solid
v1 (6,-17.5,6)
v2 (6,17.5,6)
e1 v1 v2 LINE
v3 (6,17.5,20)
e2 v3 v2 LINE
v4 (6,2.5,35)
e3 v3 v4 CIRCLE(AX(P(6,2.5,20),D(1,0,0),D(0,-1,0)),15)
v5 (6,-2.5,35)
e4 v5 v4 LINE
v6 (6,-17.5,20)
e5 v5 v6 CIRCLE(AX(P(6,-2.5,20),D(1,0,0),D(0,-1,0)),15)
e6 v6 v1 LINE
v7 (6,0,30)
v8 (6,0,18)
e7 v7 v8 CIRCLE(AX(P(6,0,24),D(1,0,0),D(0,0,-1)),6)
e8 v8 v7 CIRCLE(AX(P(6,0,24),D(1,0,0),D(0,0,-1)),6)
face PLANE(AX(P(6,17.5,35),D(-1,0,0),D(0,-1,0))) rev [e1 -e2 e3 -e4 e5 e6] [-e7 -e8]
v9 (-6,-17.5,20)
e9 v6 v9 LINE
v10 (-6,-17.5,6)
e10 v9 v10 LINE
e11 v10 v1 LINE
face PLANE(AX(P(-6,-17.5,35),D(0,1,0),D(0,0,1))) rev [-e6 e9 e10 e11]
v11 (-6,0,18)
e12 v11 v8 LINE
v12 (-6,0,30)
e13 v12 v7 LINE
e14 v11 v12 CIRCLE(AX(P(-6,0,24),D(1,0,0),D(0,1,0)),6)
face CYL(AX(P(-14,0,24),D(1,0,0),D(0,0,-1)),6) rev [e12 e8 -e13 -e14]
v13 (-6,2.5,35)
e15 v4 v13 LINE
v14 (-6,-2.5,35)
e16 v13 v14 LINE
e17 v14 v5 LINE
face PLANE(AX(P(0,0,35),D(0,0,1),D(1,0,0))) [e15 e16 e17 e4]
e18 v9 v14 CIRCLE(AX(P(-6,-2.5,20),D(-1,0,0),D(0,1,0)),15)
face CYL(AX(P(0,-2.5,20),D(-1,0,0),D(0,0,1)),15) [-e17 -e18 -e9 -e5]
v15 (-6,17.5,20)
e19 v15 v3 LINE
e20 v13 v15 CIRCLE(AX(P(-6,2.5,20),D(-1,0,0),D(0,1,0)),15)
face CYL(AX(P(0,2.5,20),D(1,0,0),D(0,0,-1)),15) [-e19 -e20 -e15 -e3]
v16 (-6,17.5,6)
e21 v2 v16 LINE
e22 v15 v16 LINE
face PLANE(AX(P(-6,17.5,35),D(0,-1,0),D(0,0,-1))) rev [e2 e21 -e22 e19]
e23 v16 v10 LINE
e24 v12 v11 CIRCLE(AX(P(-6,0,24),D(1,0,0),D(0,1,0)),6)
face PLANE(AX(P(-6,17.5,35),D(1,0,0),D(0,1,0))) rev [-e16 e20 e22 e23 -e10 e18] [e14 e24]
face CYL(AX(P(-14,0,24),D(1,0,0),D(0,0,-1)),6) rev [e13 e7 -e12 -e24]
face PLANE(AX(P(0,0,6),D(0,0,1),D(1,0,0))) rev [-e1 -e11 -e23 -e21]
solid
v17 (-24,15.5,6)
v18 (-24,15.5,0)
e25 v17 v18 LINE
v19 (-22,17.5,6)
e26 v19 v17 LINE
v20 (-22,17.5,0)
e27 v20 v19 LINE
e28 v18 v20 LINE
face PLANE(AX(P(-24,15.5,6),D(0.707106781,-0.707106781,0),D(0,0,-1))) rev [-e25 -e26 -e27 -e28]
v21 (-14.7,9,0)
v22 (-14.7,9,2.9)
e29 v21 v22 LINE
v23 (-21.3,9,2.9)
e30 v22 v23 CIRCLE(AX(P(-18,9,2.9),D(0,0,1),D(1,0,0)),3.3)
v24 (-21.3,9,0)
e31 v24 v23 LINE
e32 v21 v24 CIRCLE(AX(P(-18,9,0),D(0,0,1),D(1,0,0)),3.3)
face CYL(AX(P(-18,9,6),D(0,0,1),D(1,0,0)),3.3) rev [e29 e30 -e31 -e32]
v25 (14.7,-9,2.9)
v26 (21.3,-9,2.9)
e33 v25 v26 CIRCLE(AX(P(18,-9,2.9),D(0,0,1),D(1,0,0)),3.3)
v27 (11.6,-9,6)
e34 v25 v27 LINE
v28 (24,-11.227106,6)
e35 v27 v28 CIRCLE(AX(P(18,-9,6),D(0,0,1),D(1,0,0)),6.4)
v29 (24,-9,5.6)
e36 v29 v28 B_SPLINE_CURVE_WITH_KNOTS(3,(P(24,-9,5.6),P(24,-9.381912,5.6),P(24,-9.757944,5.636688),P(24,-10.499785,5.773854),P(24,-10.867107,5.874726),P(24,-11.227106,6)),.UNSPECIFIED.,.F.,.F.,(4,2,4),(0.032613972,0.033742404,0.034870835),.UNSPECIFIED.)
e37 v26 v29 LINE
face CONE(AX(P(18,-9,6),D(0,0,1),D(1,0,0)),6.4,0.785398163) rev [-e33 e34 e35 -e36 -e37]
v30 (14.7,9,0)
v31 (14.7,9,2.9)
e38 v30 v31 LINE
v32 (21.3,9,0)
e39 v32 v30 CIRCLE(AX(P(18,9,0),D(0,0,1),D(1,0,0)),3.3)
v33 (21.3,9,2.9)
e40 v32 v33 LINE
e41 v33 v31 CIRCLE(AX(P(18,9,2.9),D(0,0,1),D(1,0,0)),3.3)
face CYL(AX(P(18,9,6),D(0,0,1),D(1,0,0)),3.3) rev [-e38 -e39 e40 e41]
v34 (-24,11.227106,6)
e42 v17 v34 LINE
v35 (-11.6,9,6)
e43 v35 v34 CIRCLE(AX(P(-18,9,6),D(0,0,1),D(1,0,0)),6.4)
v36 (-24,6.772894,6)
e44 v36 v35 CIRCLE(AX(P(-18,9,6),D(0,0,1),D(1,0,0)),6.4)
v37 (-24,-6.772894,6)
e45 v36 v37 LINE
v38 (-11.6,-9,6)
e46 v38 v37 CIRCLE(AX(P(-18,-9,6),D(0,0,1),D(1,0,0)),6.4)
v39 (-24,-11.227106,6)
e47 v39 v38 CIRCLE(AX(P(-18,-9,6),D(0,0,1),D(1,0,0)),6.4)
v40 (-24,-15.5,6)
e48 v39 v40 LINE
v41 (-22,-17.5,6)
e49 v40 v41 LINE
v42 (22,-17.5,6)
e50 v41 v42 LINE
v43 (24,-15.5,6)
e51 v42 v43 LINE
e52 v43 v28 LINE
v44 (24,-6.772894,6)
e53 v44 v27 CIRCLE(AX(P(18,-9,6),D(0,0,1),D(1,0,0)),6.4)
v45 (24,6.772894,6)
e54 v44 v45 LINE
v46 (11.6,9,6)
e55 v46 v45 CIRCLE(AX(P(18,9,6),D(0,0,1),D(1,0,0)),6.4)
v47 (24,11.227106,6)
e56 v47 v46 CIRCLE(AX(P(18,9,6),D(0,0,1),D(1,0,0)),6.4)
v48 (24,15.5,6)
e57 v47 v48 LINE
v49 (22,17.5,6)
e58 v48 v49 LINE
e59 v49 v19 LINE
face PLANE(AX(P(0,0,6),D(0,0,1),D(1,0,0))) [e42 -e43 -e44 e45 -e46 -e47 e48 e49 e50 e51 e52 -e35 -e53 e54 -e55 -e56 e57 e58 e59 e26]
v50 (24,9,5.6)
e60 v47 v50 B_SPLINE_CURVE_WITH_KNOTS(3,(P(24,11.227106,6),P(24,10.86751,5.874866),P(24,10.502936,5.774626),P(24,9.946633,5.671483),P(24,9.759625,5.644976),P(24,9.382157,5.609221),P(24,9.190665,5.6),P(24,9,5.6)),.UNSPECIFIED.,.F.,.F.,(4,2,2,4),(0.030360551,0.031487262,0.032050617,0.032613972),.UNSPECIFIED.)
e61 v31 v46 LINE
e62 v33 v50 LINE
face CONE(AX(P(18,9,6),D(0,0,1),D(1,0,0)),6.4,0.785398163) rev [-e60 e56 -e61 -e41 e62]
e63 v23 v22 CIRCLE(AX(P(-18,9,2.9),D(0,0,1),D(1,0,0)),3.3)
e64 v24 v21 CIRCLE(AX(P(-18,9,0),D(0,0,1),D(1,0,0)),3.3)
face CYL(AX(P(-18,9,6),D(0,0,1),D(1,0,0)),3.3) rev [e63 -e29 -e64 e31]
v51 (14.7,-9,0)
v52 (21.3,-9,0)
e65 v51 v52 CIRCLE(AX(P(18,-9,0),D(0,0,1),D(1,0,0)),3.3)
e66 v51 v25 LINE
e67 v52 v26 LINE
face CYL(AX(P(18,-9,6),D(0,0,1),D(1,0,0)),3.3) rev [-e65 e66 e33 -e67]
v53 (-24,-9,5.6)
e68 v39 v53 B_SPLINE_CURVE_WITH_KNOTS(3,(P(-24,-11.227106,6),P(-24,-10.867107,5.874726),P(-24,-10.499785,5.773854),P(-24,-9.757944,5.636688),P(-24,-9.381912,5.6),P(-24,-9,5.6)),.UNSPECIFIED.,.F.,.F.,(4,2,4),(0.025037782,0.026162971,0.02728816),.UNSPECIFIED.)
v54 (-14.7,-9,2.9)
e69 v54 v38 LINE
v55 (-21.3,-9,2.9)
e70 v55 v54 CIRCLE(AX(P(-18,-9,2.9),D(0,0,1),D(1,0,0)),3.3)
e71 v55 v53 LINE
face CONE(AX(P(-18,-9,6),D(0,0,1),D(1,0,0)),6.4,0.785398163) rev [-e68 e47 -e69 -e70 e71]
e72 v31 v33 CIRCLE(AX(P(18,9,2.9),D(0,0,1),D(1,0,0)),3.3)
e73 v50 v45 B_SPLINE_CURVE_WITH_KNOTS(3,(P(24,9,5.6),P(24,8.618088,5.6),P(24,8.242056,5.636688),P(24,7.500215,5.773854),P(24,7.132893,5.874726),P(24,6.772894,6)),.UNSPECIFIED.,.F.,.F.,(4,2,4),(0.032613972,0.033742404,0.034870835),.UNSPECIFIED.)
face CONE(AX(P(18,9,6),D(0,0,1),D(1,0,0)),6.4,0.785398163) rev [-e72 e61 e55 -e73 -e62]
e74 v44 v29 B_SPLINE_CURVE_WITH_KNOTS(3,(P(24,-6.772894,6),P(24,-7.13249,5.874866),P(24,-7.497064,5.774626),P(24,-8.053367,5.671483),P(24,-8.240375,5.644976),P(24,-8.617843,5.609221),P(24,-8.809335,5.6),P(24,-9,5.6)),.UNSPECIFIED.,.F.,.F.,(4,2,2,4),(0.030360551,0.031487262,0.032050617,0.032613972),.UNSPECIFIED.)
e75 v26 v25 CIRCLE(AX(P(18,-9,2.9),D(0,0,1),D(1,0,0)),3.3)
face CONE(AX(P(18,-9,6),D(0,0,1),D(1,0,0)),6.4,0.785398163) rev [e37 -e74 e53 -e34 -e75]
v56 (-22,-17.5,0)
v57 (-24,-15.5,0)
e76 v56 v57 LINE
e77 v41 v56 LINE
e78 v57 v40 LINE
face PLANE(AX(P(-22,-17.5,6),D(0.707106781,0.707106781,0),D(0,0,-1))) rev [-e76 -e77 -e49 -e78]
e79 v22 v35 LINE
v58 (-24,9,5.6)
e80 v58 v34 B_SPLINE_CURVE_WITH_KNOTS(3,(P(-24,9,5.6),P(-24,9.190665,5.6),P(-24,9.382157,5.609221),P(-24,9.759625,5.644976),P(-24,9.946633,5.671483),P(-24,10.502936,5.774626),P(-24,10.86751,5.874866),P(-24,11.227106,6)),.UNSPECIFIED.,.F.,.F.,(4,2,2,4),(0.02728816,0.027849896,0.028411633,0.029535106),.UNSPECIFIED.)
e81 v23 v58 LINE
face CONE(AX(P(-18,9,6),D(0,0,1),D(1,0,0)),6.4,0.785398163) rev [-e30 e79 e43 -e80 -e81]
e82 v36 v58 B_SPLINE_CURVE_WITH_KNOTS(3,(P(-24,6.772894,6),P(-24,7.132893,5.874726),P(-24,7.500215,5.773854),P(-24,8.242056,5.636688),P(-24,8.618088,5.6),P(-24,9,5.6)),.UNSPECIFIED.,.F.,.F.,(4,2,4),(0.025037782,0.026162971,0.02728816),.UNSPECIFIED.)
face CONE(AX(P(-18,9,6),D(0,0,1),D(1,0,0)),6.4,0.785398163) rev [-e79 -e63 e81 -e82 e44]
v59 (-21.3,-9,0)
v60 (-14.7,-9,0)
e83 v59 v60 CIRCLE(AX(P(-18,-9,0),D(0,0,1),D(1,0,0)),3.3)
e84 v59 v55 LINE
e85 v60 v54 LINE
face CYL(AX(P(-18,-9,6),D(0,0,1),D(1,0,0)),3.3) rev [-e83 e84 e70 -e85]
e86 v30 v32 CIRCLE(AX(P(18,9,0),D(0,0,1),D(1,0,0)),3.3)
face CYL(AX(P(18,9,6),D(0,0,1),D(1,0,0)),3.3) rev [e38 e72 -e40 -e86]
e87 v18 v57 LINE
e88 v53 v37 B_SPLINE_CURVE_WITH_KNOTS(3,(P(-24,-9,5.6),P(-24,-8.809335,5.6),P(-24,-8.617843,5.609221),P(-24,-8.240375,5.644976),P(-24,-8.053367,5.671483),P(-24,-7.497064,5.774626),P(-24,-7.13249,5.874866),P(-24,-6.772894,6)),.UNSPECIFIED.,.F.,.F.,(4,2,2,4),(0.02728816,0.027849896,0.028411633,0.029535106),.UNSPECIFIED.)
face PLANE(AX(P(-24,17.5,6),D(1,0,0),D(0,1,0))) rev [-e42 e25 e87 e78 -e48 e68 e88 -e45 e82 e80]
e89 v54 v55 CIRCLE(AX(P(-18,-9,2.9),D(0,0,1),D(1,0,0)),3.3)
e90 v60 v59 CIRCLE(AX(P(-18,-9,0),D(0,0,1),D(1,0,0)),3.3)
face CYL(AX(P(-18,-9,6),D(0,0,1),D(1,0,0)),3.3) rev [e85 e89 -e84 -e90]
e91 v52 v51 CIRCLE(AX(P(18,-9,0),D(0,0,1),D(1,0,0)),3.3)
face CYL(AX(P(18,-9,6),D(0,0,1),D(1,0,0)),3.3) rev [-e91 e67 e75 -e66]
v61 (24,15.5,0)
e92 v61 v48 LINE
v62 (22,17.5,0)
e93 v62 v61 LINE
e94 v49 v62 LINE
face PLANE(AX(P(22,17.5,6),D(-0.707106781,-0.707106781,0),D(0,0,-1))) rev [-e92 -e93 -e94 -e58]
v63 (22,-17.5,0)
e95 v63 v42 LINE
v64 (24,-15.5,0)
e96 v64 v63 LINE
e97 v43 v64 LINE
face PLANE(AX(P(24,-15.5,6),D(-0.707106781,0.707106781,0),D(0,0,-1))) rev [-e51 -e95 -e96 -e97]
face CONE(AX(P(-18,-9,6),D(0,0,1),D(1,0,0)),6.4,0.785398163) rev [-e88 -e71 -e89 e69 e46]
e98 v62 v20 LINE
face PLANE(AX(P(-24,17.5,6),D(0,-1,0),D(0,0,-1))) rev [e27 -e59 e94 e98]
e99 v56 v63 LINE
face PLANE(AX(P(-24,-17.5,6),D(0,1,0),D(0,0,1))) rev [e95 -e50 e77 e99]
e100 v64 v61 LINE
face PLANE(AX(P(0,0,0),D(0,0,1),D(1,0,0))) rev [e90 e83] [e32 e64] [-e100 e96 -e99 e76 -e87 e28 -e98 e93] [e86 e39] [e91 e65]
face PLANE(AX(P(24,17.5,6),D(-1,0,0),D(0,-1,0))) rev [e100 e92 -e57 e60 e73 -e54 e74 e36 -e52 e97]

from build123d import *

# Parameters (mm, degrees)
SKETCH1_W                                    = 48
SKETCH1_H                                    = 35
BOSS_EXTRUDE1_DEPTH                          = 6
SKETCH2_W                                    = 12
SKETCH2_H                                    = 35
BOSS_EXTRUDE2_DEPTH                          = 29
FILLET1_R                                    = 15
SKETCH3_R                                    = 6
CUT_EXTRUDE1_DEPTH                           = 20
CHAMFER1_SIZE                                = 2
HOLE_SIZE_SLOTTED_RAISED_COUNTERSUNK_2_COUNT = 2
HOLE_SIZE_SLOTTED_RAISED_COUNTERSUNK_2_PITCH = 18
HOLE_SIZE_SLOTTED_RAISED_COUNTERSUNK_3_COUNT = 2
HOLE_SIZE_SLOTTED_RAISED_COUNTERSUNK_3_PITCH = 36
HOLE_SIZE_SLOTTED_RAISED_COUNTERSUNK_4_COUNT = 2
HOLE_SIZE_SLOTTED_RAISED_COUNTERSUNK_4_PITCH = 40.249223595


with BuildPart() as part:
    # Sketch1 → Boss-Extrude1 (new body)
    with BuildSketch(Plane.XY):
        Rectangle(SKETCH1_W, SKETCH1_H)
    extrude(amount=BOSS_EXTRUDE1_DEPTH)

    # Chamfer1
    chamfer1_edges = [part.edges().sort_by_distance(p)[0] for p in [
        (24, -17.5, 3),
        (-24, -17.5, 3),
        (-24, 17.5, 3),
        (24, 17.5, 3),
    ]]
    chamfer(chamfer1_edges, length=CHAMFER1_SIZE)

    # Sketch5 → Hole Size slotted raised countersunk screw type 1 (revolve, cut)
    with BuildSketch(Plane(origin=(-18, 9, 6), x_dir=(0, -1, 0), z_dir=(1, 0, 0))):
        Polygon((0, 0), (0, 6), (3.3, 6), (3.3, 3.1), (6.4, 0), align=None)
    hole_size_slotted_raised_countersunk_scr = revolve(axis=Axis((-18, 9, 12.35), (0, 0, -1)), mode=Mode.SUBTRACT)

    # Hole Size slotted raised countersunk 2: Hole Size slotted raised countersunk screw type 1 ×2
    with Locations(*[(0, -i * HOLE_SIZE_SLOTTED_RAISED_COUNTERSUNK_2_PITCH, 0) for i in range(1, HOLE_SIZE_SLOTTED_RAISED_COUNTERSUNK_2_COUNT)]):
        add(hole_size_slotted_raised_countersunk_scr, mode=Mode.SUBTRACT)

    # Hole Size slotted raised countersunk 3: Hole Size slotted raised countersunk screw type 1 ×2
    with Locations(*[(i * HOLE_SIZE_SLOTTED_RAISED_COUNTERSUNK_3_PITCH, 0, 0) for i in range(1, HOLE_SIZE_SLOTTED_RAISED_COUNTERSUNK_3_COUNT)]):
        add(hole_size_slotted_raised_countersunk_scr, mode=Mode.SUBTRACT)

    # Hole Size slotted raised countersunk 4: Hole Size slotted raised countersunk screw type 1 ×2
    with Locations(*[Vector(0.894427190999916, -0.447213595499958, 0) * (i * HOLE_SIZE_SLOTTED_RAISED_COUNTERSUNK_4_PITCH) for i in range(1, HOLE_SIZE_SLOTTED_RAISED_COUNTERSUNK_4_COUNT)]):
        add(hole_size_slotted_raised_countersunk_scr, mode=Mode.SUBTRACT)


with BuildPart() as body_2:
    # Sketch2 → Boss-Extrude2 (new body)
    with BuildSketch(Plane.XY.offset(6)):
        Rectangle(SKETCH2_W, SKETCH2_H)
    extrude(amount=BOSS_EXTRUDE2_DEPTH)

    # Fillet1
    fillet1_edges = [body_2.edges().sort_by_distance(p)[0] for p in [
        (0, -17.5, 35),
        (0, 17.5, 35),
    ]]
    fillet(fillet1_edges, radius=FILLET1_R)

    # Sketch3 → Cut-Extrude1 (cut)
    with BuildSketch(Plane(origin=(6, 0, 0), x_dir=(0, 0, -1), z_dir=(1, 0, 0))):
        with Locations((-24, 0)):
            Circle(SKETCH3_R)
    extrude(amount=-CUT_EXTRUDE1_DEPTH, mode=Mode.SUBTRACT)


solid = Compound([part.part, body_2.part])
